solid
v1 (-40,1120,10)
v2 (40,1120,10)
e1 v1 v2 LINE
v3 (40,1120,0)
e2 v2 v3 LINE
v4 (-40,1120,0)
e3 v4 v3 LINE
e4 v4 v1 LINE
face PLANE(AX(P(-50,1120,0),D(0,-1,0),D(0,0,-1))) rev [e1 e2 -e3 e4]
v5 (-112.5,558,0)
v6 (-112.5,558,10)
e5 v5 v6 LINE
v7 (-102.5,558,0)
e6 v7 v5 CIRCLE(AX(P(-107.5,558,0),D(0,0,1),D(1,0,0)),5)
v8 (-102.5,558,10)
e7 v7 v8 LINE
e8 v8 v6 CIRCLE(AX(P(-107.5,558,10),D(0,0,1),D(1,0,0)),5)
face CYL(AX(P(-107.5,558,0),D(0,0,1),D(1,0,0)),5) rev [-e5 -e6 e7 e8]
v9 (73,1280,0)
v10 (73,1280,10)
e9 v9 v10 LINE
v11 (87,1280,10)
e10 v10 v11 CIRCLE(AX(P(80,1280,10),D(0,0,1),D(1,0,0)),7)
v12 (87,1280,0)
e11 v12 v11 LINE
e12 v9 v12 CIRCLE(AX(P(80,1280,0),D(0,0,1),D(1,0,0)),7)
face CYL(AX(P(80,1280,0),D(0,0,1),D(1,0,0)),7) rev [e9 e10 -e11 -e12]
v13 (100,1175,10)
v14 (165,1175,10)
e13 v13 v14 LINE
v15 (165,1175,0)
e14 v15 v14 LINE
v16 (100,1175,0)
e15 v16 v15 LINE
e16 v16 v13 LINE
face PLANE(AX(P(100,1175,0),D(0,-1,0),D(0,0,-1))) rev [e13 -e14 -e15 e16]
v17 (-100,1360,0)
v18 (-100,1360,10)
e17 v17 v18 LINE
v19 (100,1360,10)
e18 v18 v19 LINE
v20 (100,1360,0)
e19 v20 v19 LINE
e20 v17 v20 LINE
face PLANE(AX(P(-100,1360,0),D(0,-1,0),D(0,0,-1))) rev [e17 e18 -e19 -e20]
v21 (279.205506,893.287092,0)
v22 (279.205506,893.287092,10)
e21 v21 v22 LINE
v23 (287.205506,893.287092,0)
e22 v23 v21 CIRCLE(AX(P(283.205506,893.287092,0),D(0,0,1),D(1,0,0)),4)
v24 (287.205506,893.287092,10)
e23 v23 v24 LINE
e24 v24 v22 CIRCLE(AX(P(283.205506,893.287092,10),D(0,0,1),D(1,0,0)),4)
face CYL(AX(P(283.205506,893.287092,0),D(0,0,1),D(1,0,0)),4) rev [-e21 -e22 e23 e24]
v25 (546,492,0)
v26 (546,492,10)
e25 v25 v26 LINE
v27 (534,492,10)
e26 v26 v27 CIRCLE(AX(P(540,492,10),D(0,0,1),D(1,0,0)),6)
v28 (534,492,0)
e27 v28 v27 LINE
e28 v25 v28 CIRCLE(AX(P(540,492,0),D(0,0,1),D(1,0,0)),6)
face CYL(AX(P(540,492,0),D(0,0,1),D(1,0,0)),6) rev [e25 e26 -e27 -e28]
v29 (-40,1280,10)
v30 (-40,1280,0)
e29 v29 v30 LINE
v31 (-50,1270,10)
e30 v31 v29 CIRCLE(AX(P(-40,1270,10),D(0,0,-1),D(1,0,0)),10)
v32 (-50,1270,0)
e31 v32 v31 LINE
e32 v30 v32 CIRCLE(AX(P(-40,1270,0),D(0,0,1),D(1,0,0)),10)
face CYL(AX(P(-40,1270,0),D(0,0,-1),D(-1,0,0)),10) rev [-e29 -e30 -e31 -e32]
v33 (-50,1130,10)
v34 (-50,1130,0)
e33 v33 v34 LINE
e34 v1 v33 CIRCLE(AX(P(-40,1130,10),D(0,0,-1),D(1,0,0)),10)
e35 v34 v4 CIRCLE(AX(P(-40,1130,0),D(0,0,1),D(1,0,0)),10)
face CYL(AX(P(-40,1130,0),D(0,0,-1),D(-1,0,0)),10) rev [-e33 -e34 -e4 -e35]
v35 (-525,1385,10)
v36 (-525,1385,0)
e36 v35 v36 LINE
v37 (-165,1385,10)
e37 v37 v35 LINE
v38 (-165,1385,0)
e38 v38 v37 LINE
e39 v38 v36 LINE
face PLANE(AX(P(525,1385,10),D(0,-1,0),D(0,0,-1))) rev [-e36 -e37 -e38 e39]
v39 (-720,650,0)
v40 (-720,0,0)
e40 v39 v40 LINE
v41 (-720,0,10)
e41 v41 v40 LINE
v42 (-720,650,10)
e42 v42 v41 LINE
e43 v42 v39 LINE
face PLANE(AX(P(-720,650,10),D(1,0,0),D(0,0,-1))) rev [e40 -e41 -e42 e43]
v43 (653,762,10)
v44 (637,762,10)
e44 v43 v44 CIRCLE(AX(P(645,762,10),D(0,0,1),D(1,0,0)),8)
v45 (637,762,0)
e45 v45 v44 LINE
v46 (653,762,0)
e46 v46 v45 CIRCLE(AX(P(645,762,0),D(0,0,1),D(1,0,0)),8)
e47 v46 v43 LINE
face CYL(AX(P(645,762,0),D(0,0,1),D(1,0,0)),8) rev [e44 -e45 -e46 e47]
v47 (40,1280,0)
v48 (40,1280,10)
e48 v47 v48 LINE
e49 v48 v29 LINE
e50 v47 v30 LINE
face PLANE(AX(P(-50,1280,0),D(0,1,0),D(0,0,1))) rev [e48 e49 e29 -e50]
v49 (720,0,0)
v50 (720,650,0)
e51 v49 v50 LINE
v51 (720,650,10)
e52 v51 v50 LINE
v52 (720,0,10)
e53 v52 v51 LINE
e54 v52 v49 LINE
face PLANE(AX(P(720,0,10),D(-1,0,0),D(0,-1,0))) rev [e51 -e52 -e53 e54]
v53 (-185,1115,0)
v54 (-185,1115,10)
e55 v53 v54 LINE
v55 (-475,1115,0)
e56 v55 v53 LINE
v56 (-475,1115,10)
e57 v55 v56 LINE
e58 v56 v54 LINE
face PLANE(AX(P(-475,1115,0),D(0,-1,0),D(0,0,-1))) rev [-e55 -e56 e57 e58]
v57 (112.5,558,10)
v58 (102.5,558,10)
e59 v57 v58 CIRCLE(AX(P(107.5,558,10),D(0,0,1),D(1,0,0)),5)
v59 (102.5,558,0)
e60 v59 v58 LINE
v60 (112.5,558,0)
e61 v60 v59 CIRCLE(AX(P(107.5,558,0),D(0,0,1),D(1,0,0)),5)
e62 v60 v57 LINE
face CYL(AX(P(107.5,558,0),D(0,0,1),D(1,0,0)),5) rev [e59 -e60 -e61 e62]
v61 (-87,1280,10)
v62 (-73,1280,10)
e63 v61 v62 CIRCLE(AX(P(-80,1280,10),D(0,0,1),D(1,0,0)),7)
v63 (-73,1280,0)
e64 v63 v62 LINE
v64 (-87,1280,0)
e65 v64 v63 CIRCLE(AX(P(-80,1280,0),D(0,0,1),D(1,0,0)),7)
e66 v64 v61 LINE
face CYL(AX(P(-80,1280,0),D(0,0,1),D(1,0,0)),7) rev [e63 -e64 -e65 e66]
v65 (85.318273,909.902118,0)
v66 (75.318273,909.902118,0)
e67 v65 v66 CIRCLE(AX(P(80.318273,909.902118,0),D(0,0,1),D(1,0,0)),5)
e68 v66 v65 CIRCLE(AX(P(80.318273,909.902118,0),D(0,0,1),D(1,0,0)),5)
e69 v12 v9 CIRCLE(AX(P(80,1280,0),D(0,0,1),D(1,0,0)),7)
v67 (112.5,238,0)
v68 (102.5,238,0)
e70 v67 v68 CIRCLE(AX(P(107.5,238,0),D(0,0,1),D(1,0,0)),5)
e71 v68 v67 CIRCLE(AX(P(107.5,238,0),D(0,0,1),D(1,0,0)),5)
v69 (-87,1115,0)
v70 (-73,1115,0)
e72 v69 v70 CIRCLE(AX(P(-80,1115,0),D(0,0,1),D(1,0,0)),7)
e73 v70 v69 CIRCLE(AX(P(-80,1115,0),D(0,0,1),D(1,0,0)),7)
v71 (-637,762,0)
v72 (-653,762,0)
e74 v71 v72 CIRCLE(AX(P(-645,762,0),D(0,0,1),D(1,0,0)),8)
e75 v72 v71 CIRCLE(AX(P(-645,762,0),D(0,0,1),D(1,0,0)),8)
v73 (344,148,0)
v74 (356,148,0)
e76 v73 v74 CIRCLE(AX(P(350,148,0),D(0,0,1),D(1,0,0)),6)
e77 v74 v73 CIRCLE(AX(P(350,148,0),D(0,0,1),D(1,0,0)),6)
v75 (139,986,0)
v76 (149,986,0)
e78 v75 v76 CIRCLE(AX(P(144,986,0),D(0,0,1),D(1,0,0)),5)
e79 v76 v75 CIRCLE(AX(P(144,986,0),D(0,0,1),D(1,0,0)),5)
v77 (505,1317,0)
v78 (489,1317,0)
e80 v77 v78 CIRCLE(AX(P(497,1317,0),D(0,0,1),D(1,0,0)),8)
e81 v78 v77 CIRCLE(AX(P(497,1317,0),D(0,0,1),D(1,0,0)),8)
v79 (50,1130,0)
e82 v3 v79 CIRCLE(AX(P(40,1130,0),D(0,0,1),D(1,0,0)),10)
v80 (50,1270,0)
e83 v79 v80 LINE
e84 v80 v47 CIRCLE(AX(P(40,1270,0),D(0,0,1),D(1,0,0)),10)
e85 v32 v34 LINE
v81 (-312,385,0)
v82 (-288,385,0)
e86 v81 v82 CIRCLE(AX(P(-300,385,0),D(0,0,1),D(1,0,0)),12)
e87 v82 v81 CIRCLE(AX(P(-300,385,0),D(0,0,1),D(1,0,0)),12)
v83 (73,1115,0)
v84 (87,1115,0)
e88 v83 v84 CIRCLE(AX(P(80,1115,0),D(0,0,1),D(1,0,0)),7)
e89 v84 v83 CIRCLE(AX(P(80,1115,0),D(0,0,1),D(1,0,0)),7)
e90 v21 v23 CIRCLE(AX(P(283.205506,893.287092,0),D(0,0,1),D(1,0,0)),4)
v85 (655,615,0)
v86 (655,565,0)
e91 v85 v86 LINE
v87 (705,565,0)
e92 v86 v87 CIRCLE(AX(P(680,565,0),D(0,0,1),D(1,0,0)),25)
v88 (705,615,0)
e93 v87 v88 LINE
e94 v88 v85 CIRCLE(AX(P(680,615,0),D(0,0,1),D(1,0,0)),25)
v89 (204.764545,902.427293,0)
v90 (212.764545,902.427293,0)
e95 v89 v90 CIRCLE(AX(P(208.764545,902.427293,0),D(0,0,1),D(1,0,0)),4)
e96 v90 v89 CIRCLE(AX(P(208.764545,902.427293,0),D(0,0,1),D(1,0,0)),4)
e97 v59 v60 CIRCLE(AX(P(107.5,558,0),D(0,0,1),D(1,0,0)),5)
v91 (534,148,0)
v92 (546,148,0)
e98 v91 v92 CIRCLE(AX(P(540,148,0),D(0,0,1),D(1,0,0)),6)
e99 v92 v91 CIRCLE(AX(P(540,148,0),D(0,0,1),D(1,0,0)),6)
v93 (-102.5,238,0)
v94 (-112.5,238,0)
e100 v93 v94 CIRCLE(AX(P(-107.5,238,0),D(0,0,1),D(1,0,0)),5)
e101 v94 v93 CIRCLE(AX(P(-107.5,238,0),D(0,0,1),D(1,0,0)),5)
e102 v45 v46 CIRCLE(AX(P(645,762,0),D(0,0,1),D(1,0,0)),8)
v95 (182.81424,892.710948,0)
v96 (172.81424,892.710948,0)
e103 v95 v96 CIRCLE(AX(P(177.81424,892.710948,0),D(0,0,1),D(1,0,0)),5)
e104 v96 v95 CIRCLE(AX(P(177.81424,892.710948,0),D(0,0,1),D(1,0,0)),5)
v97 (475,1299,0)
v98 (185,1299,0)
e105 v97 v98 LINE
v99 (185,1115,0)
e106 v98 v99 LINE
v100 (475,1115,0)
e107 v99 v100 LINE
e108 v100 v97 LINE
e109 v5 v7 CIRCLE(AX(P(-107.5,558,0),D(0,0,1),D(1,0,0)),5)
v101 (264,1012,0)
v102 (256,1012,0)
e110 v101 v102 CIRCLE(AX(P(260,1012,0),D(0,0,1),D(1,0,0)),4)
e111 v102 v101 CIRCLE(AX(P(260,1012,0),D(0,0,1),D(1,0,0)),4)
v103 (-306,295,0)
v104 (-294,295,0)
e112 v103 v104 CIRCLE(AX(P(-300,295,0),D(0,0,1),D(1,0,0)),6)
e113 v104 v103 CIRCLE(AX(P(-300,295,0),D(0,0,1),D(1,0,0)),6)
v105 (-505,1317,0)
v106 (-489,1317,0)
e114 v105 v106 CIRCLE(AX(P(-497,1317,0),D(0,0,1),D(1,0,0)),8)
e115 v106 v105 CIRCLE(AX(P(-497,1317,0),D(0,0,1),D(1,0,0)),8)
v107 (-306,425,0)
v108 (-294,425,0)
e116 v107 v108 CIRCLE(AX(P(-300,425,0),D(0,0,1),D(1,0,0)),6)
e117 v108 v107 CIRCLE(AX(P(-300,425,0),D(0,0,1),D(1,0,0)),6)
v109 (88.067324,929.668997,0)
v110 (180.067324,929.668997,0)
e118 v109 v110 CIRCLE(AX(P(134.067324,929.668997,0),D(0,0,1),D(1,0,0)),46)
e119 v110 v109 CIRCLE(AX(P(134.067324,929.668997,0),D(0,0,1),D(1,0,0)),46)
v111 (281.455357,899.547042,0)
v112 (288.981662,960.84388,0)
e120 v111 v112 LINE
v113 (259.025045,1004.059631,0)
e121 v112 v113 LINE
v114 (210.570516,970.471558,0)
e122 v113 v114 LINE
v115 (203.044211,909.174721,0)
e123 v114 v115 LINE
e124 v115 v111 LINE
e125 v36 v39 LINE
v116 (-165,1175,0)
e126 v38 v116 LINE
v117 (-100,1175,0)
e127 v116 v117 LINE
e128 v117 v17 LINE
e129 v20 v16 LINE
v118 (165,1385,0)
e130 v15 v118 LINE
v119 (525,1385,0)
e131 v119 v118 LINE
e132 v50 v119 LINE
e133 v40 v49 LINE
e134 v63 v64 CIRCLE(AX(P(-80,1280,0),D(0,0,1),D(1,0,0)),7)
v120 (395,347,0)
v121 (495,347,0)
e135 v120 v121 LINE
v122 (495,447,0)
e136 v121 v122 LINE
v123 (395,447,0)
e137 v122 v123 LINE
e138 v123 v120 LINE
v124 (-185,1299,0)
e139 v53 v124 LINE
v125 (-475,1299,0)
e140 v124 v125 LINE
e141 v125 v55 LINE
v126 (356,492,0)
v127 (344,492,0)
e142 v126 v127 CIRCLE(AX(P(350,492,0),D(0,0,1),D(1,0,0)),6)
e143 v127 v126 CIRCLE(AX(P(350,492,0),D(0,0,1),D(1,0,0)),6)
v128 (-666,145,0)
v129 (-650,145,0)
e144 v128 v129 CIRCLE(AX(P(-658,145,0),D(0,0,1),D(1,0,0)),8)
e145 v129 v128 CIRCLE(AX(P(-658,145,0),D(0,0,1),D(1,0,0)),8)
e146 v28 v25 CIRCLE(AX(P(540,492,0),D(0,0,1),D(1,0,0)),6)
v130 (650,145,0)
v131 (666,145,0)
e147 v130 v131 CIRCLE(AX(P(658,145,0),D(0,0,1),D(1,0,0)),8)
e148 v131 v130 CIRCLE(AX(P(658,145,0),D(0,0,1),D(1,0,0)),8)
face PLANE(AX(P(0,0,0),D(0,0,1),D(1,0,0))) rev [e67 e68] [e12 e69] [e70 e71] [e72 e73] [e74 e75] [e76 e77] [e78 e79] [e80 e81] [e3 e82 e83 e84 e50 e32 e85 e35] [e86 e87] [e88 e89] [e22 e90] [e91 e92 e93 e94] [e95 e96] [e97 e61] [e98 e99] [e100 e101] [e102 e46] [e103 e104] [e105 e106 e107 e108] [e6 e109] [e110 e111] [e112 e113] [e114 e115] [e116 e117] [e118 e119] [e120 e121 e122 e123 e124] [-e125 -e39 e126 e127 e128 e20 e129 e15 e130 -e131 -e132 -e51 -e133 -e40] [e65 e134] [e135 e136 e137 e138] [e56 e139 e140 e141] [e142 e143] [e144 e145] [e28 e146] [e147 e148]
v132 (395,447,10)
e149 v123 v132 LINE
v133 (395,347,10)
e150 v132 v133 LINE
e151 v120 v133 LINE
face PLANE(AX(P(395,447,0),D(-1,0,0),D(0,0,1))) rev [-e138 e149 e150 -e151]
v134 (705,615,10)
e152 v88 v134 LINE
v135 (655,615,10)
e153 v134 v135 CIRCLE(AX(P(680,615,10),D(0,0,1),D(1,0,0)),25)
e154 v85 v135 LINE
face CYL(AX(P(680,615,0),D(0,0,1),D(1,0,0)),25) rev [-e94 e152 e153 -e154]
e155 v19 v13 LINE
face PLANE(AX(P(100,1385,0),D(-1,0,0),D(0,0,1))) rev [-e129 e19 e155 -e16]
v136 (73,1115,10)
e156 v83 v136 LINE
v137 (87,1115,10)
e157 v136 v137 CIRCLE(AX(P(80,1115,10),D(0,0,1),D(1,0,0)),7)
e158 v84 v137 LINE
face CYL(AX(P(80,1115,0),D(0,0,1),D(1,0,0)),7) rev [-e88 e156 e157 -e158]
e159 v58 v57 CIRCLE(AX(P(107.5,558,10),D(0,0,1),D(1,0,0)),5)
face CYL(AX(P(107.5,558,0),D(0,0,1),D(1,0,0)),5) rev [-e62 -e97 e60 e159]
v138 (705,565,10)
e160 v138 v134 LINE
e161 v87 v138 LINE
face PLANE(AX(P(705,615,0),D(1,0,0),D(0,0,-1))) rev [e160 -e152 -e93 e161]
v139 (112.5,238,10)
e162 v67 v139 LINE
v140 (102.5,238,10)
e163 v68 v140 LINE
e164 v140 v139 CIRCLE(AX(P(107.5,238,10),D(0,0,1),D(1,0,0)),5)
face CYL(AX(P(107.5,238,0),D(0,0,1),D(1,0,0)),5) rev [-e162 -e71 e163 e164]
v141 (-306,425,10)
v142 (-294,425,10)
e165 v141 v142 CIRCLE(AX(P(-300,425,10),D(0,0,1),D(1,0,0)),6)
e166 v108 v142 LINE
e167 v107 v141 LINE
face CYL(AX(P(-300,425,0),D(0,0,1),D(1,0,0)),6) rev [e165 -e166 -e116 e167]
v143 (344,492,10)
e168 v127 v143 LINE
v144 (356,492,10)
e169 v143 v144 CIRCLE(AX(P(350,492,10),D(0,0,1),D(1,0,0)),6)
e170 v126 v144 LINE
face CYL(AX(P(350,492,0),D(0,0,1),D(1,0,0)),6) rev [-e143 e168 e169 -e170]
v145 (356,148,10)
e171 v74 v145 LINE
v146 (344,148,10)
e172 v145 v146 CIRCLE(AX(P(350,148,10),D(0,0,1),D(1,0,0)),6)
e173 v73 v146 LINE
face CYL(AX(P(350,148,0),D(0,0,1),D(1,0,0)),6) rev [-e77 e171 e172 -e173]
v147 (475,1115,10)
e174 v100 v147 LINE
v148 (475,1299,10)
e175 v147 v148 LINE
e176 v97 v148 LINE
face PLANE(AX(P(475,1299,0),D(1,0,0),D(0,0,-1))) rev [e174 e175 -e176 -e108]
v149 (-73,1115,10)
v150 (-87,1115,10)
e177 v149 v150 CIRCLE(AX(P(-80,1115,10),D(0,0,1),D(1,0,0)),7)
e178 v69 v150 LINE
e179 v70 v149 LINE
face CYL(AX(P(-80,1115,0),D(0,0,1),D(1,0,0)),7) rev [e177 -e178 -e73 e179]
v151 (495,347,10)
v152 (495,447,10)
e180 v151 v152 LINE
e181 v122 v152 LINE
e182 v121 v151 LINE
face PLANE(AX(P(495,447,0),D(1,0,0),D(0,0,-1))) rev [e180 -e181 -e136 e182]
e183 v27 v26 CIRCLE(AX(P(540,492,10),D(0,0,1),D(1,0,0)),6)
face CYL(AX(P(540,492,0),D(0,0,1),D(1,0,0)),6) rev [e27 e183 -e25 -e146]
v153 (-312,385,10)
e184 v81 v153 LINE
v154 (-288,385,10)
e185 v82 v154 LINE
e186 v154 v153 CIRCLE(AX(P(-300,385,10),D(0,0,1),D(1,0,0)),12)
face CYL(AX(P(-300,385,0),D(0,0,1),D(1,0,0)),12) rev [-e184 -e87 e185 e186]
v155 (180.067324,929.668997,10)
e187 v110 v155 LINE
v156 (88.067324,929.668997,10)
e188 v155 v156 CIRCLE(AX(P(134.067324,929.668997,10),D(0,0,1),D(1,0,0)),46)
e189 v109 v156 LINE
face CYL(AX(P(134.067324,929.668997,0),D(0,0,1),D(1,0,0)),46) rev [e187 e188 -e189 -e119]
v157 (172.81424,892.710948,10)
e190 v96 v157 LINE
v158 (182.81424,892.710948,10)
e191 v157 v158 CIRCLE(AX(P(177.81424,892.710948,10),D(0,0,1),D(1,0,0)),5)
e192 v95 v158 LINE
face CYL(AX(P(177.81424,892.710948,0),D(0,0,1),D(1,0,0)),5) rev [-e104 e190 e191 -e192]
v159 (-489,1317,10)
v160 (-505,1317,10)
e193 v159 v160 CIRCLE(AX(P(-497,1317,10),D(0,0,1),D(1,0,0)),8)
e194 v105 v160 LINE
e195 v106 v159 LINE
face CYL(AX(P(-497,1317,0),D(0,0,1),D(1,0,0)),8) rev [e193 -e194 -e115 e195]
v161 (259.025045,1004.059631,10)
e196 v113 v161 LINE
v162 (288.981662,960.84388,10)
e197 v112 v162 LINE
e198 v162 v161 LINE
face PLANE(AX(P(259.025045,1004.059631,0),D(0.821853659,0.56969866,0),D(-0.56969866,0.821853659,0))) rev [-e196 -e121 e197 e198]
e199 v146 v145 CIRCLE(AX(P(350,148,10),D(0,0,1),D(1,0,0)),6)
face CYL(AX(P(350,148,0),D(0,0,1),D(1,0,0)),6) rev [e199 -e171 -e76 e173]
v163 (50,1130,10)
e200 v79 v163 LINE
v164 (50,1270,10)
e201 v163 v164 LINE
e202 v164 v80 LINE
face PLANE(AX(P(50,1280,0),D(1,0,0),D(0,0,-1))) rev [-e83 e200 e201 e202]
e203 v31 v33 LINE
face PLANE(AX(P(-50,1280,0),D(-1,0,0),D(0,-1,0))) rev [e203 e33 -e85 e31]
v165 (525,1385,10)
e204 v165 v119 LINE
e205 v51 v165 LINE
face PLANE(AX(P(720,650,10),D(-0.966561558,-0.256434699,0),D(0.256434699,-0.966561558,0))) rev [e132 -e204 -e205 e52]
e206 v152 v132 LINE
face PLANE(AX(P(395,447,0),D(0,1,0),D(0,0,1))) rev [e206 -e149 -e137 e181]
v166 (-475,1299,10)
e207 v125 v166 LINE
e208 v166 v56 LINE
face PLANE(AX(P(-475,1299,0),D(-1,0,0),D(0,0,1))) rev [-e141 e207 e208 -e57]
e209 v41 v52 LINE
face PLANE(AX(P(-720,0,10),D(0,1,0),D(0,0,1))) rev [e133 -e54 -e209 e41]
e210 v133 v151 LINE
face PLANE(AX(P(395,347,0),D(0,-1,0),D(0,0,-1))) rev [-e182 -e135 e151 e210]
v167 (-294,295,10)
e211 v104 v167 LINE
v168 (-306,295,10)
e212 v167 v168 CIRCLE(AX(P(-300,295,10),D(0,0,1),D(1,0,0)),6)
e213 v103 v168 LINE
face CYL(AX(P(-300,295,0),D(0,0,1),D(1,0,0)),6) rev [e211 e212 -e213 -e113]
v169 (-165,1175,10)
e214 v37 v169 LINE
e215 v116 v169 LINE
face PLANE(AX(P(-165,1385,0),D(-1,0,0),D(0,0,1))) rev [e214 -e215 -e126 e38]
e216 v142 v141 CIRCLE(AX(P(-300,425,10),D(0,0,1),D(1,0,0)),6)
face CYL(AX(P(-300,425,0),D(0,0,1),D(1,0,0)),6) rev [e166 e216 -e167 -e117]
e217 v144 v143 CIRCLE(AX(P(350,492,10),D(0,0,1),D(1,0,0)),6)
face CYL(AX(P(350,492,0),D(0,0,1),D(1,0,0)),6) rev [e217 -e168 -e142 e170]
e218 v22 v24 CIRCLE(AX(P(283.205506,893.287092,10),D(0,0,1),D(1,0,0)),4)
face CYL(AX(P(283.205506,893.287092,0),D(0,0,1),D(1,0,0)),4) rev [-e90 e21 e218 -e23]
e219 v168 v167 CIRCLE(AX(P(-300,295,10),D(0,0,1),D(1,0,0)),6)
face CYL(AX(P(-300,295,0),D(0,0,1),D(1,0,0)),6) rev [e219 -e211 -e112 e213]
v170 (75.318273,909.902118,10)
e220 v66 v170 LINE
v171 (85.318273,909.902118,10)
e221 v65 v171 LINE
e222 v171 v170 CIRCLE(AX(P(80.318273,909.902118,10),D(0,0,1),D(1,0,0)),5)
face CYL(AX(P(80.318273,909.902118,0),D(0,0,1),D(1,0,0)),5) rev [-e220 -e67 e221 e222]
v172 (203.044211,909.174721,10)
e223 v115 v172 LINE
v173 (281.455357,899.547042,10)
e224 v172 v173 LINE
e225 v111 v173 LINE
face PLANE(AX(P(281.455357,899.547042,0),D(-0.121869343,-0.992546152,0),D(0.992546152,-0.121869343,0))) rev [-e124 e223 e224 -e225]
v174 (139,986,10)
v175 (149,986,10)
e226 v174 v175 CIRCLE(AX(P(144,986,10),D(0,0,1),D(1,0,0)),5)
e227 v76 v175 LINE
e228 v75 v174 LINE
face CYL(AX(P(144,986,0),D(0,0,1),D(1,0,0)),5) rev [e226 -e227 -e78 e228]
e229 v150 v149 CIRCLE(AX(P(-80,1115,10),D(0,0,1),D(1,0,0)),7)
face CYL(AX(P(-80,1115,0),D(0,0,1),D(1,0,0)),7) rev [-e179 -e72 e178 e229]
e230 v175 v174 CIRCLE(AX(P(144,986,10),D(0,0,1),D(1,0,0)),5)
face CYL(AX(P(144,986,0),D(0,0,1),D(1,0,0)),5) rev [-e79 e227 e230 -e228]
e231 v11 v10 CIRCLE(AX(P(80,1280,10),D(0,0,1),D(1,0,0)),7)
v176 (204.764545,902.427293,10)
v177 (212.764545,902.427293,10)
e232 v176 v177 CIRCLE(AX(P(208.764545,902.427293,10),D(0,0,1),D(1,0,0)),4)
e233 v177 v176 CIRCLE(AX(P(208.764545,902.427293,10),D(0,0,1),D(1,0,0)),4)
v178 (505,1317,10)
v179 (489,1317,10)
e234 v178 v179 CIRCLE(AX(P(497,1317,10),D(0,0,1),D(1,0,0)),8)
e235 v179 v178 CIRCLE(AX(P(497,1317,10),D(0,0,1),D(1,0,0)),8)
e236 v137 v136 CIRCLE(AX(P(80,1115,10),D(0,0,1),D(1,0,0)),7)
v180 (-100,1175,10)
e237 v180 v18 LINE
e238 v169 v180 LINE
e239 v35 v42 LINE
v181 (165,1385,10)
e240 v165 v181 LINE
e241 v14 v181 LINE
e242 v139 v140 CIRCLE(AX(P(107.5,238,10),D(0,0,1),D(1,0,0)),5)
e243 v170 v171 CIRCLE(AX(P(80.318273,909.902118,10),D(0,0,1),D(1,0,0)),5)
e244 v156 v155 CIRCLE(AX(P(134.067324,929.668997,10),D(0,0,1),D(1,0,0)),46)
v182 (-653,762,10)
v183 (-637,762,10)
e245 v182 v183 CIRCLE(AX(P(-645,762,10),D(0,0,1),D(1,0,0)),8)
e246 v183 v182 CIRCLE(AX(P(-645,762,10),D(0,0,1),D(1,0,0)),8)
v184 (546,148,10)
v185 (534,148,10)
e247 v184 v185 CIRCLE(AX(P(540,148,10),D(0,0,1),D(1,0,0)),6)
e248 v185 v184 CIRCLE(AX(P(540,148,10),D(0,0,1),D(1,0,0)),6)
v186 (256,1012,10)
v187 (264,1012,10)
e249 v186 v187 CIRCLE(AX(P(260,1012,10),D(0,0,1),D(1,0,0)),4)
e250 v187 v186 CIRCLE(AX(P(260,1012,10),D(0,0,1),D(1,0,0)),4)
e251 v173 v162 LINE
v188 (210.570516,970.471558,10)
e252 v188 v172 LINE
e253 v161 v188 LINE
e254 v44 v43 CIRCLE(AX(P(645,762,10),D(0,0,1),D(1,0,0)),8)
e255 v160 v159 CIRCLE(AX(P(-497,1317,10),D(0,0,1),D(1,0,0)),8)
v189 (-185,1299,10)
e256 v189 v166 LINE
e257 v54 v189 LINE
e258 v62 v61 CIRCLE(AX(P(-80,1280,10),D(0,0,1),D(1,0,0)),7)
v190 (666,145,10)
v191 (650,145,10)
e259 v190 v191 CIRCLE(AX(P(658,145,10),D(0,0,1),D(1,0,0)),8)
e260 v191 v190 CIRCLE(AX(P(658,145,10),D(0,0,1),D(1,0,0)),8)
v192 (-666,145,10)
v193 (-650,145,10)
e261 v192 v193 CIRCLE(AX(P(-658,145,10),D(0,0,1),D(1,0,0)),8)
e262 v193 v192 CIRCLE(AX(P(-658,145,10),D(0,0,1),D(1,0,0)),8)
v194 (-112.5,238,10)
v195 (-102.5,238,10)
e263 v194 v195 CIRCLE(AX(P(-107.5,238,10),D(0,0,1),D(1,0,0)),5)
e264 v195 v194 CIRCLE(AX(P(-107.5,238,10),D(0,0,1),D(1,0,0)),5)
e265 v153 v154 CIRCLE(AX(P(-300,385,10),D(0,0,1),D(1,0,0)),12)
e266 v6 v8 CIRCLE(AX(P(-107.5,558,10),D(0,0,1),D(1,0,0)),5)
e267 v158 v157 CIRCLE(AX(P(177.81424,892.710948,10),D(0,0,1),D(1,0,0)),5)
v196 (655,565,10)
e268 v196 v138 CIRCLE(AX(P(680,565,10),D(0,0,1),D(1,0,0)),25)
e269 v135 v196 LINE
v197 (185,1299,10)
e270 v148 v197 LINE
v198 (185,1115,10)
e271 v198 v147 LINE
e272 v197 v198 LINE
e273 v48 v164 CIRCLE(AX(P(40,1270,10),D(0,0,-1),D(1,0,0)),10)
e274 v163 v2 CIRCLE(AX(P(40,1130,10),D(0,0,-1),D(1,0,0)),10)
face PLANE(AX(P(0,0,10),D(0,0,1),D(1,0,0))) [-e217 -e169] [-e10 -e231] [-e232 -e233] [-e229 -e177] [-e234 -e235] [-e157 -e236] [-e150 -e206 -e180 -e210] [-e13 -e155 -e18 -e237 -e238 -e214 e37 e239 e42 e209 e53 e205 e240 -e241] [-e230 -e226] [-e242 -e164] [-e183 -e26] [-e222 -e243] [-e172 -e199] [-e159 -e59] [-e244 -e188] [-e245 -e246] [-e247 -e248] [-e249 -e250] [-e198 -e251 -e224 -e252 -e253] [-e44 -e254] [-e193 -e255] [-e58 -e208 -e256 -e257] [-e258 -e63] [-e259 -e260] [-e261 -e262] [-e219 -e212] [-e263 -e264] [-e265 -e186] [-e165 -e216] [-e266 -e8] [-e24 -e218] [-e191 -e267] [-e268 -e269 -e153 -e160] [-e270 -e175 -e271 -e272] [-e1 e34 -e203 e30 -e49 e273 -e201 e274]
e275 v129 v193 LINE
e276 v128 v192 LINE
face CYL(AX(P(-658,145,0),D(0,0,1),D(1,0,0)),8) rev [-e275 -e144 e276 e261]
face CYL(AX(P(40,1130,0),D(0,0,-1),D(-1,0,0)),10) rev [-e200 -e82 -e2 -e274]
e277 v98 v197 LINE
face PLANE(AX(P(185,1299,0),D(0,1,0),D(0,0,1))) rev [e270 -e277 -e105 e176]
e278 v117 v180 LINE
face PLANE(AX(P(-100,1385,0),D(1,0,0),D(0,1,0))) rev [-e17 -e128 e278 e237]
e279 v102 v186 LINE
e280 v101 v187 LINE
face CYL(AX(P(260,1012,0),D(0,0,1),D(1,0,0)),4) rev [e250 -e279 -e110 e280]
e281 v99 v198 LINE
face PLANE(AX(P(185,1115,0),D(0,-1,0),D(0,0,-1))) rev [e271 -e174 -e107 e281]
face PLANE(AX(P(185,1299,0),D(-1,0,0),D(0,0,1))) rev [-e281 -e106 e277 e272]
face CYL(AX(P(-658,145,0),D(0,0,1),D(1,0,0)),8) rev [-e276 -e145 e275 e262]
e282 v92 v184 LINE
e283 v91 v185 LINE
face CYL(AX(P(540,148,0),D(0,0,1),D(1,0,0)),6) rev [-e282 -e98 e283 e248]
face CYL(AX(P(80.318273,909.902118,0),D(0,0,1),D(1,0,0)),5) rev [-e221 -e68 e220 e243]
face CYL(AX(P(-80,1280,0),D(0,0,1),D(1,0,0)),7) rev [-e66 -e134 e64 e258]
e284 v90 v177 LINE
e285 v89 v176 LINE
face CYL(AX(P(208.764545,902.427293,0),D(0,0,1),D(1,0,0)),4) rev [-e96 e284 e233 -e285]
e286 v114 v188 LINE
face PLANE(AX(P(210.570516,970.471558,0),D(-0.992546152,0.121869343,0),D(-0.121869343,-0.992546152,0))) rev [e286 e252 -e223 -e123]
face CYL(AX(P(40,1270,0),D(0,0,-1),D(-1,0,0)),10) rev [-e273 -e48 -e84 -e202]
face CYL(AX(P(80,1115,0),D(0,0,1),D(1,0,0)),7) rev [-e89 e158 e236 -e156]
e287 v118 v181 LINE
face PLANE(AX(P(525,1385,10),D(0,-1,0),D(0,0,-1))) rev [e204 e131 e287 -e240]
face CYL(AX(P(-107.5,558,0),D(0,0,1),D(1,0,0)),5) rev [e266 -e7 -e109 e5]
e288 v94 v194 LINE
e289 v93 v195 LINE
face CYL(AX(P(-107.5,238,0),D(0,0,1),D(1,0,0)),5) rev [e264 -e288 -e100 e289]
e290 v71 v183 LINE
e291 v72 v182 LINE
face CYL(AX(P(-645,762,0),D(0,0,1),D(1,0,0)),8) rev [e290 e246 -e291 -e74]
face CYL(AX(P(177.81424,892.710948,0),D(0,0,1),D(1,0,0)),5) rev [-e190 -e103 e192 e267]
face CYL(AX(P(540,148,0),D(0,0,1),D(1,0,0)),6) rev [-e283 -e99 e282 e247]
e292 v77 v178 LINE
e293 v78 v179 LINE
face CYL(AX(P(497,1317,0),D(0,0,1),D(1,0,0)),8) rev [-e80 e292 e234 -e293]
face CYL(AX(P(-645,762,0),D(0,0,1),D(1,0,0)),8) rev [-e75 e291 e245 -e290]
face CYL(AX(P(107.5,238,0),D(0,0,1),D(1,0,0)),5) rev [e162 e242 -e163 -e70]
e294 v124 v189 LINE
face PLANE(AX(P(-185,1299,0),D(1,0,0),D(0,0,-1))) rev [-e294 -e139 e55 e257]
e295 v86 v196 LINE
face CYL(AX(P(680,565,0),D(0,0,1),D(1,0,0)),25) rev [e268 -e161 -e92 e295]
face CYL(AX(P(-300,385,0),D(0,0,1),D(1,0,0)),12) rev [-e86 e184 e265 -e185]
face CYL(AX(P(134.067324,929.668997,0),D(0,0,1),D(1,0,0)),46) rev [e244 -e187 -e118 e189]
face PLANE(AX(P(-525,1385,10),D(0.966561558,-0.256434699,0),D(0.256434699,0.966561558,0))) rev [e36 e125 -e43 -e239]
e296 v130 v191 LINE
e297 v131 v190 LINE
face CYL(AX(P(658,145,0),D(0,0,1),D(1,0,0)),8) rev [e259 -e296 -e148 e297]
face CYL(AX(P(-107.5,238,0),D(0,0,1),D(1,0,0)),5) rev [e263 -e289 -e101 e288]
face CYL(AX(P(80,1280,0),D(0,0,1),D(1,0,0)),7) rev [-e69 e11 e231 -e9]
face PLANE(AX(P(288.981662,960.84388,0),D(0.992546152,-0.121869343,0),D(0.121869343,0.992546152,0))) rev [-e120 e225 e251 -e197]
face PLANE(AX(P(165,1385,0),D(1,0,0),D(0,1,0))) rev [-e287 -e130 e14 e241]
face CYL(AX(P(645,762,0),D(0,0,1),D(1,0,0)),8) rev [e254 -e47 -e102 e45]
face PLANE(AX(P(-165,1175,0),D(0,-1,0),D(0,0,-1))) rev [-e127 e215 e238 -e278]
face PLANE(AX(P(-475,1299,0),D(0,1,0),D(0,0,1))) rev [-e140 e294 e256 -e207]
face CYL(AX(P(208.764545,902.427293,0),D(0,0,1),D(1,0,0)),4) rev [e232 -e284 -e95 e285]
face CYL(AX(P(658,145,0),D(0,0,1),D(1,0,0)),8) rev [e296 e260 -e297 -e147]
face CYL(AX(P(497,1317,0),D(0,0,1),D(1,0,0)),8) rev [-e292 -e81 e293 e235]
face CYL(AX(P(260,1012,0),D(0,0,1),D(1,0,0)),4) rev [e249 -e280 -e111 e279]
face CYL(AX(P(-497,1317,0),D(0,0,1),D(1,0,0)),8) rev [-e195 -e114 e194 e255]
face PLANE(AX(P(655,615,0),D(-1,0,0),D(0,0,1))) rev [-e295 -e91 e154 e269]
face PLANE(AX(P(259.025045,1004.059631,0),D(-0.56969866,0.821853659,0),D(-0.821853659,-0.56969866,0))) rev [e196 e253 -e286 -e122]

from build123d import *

# Parameters (mm, degrees)
BOSS_EXTRUDE1_DEPTH  = 10
SKETCH2_R            = 8
CUT_EXTRUDE1_DEPTH   = 10
LPATTERN1_COUNT      = 2
LPATTERN1_PITCH      = 1316
SKETCH3_R            = 8
CUT_EXTRUDE2_DEPTH   = 10
LPATTERN2_COUNT      = 2
LPATTERN2_PITCH      = 1290
SKETCH4_R            = 8
CUT_EXTRUDE3_DEPTH   = 10
LPATTERN3_COUNT      = 2
LPATTERN3_PITCH      = 994
CUT_EXTRUDE4_DEPTH   = 10
SKETCH6_W            = 100
SKETCH6_H            = 100
CUT_EXTRUDE5_DEPTH   = 10
SKETCH7_R            = 6
CUT_EXTRUDE6_DEPTH   = 10
LPATTERN4_COUNT      = 2
LPATTERN4_PITCH      = 190
LPATTERN4_COUNT_DIR2 = 2
LPATTERN4_PITCH_DIR2 = 344
SKETCH8_R            = 5
CUT_EXTRUDE7_DEPTH   = 10
LPATTERN5_COUNT      = 2
LPATTERN5_PITCH      = 320
LPATTERN5_COUNT_DIR2 = 2
LPATTERN5_PITCH_DIR2 = 215
SKETCH9_W            = 290
SKETCH9_H            = 184
CUT_EXTRUDE8_DEPTH   = 10
SKETCH10_W           = 100
SKETCH10_H           = 160
CUT_EXTRUDE9_DEPTH   = 10
FILLET1_R            = 10
SKETCH11_R           = 7
CUT_EXTRUDE10_DEPTH  = 10
LPATTERN7_COUNT      = 2
LPATTERN7_PITCH      = 160
LPATTERN7_COUNT_DIR2 = 2
LPATTERN7_PITCH_DIR2 = 165
SKETCH12_R           = 5
CUT_EXTRUDE11_DEPTH  = 10
SKETCH14_R           = 46
CUT_EXTRUDE12_DEPTH  = 10
SKETCH15_R           = 5
CUT_EXTRUDE13_DEPTH  = 10
LPATTERN8_COUNT      = 2
LPATTERN8_PITCH      = 99
SKETCH16_R           = 4
CUT_EXTRUDE14_DEPTH  = 10
CUT_EXTRUDE15_DEPTH  = 10
SKETCH18_R           = 4
CUT_EXTRUDE16_DEPTH  = 10
LPATTERN9_COUNT      = 2
LPATTERN9_PITCH      = 75
SKETCH19_R           = 6
CUT_EXTRUDE17_DEPTH  = 10
LPATTERN10_COUNT     = 2
LPATTERN10_PITCH     = 130
SKETCH20_R           = 12
CUT_EXTRUDE18_DEPTH  = 10
LPATTERN11_COUNT     = 2
LPATTERN11_PITCH     = 660
SKETCH21_W           = 65
SKETCH21_H           = 210
CUT_EXTRUDE19_DEPTH  = 10
SKETCH22_W           = 65
SKETCH22_H           = 210
CUT_EXTRUDE20_DEPTH  = 10
SKETCH23_W           = 200
SKETCH23_H           = 25
CUT_EXTRUDE21_DEPTH  = 10


with BuildPart() as part:
    # Sketch1 → Boss-Extrude1 (new body)
    with BuildSketch(Plane.XY):
        Polygon((-720, 0), (720, 0), (720, 650), (525, 1385), (-525, 1385), (-720, 650), align=None)
    extrude(amount=BOSS_EXTRUDE1_DEPTH)

    # Sketch2 → Cut-Extrude1 (cut)
    with BuildSketch(Plane.XY.offset(10)):
        with Locations((-658, 145)):
            Circle(SKETCH2_R)
    cut_extrude1 = extrude(amount=-CUT_EXTRUDE1_DEPTH, mode=Mode.SUBTRACT)

    # LPattern1: Cut-Extrude1 ×2
    with Locations(*[(i * LPATTERN1_PITCH, 0, 0) for i in range(1, LPATTERN1_COUNT)]):
        add(cut_extrude1, mode=Mode.SUBTRACT)

    # Sketch3 → Cut-Extrude2 (cut)
    with BuildSketch(Plane.XY.offset(10)):
        with Locations((-645, 762)):
            Circle(SKETCH3_R)
    cut_extrude2 = extrude(amount=-CUT_EXTRUDE2_DEPTH, mode=Mode.SUBTRACT)

    # LPattern2: Cut-Extrude2 ×2
    with Locations(*[(i * LPATTERN2_PITCH, 0, 0) for i in range(1, LPATTERN2_COUNT)]):
        add(cut_extrude2, mode=Mode.SUBTRACT)

    # Sketch4 → Cut-Extrude3 (cut)
    with BuildSketch(Plane.XY.offset(10)):
        with Locations((-497, 1317)):
            Circle(SKETCH4_R)
    cut_extrude3 = extrude(amount=-CUT_EXTRUDE3_DEPTH, mode=Mode.SUBTRACT)

    # LPattern3: Cut-Extrude3 ×2
    with Locations(*[(i * LPATTERN3_PITCH, 0, 0) for i in range(1, LPATTERN3_COUNT)]):
        add(cut_extrude3, mode=Mode.SUBTRACT)

    # Sketch5 → Cut-Extrude4 (cut)
    with BuildSketch(Plane.XY.offset(10)):
        with BuildLine():
            Line((655, 615), (655, 565))
            ThreePointArc((655, 565), (680, 540), (705, 565))
            Line((705, 565), (705, 615))
            ThreePointArc((705, 615), (680, 640), (655, 615))
        make_face()
    extrude(amount=-CUT_EXTRUDE4_DEPTH, mode=Mode.SUBTRACT)

    # Sketch6 → Cut-Extrude5 (cut)
    with BuildSketch(Plane.XY.offset(10)):
        with Locations((445, 397)):
            Rectangle(SKETCH6_W, SKETCH6_H)
    extrude(amount=-CUT_EXTRUDE5_DEPTH, mode=Mode.SUBTRACT)

    # Sketch7 → Cut-Extrude6 (cut)
    with BuildSketch(Plane.XY.offset(10)):
        with Locations((540, 492)):
            Circle(SKETCH7_R)
    cut_extrude6 = extrude(amount=-CUT_EXTRUDE6_DEPTH, mode=Mode.SUBTRACT)

    # LPattern4: Cut-Extrude6 2 × 2
    with Locations(*[(-i * LPATTERN4_PITCH, -j * LPATTERN4_PITCH_DIR2, 0) for i in range(LPATTERN4_COUNT) for j in range(LPATTERN4_COUNT_DIR2) if (i, j) != (0, 0)]):
        add(cut_extrude6, mode=Mode.SUBTRACT)

    # Sketch8 → Cut-Extrude7 (cut)
    with BuildSketch(Plane.XY.offset(10)):
        with Locations((107.5, 238)):
            Circle(SKETCH8_R)
    cut_extrude7 = extrude(amount=-CUT_EXTRUDE7_DEPTH, mode=Mode.SUBTRACT)

    # LPattern5: Cut-Extrude7 2 × 2
    with Locations(*[(-j * LPATTERN5_PITCH_DIR2, i * LPATTERN5_PITCH, 0) for i in range(LPATTERN5_COUNT) for j in range(LPATTERN5_COUNT_DIR2) if (i, j) != (0, 0)]):
        add(cut_extrude7, mode=Mode.SUBTRACT)

    # Sketch9 → Cut-Extrude8 (cut)
    with BuildSketch(Plane.XY.offset(10)):
        with Locations((-330, 1207)):
            Rectangle(SKETCH9_W, SKETCH9_H)
    cut_extrude8 = extrude(amount=-CUT_EXTRUDE8_DEPTH, mode=Mode.SUBTRACT)

    # Sketch10 → Cut-Extrude9 (cut)
    with BuildSketch(Plane.XY.offset(10)):
        with Locations((0, 1200)):
            Rectangle(SKETCH10_W, SKETCH10_H)
    extrude(amount=-CUT_EXTRUDE9_DEPTH, mode=Mode.SUBTRACT)

    # Fillet1
    fillet1_edges = [part.edges().sort_by_distance(p)[0] for p in [
        (-50, 1120, 5),
        (-50, 1280, 5),
        (50, 1280, 5),
        (50, 1120, 5),
    ]]
    fillet(fillet1_edges, radius=FILLET1_R)

    # Sketch11 → Cut-Extrude10 (cut)
    with BuildSketch(Plane.XY.offset(10)):
        with Locations((80, 1280)):
            Circle(SKETCH11_R)
    cut_extrude10 = extrude(amount=-CUT_EXTRUDE10_DEPTH, mode=Mode.SUBTRACT)

    # LPattern7: Cut-Extrude10 2 × 2
    with Locations(*[(-i * LPATTERN7_PITCH, -j * LPATTERN7_PITCH_DIR2, 0) for i in range(LPATTERN7_COUNT) for j in range(LPATTERN7_COUNT_DIR2) if (i, j) != (0, 0)]):
        add(cut_extrude10, mode=Mode.SUBTRACT)

    # Sketch12 → Cut-Extrude11 (cut)
    with BuildSketch(Plane.XY.offset(10)):
        with Locations((144, 986)):
            Circle(SKETCH12_R)
    extrude(amount=-CUT_EXTRUDE11_DEPTH, mode=Mode.SUBTRACT)

    # Sketch14 → Cut-Extrude12 (cut)
    with BuildSketch(Plane.XY.offset(10)):
        with Locations((134.067324237, 929.668996528)):
            Circle(SKETCH14_R)
    extrude(amount=-CUT_EXTRUDE12_DEPTH, mode=Mode.SUBTRACT)

    # Sketch15 → Cut-Extrude13 (cut)
    with BuildSketch(Plane.XY.offset(10)):
        with Locations((80.318272947, 909.902118035)):
            Circle(SKETCH15_R)
    cut_extrude13 = extrude(amount=-CUT_EXTRUDE13_DEPTH, mode=Mode.SUBTRACT)

    # LPattern8: Cut-Extrude13 ×2
    with Locations(*[Vector(0.9848077530122089, -0.17364817766692592, 0) * (i * LPATTERN8_PITCH) for i in range(1, LPATTERN8_COUNT)]):
        add(cut_extrude13, mode=Mode.SUBTRACT)

    # Sketch16 → Cut-Extrude14 (cut)
    with BuildSketch(Plane.XY.offset(10)):
        with Locations((260, 1012)):
            Circle(SKETCH16_R)
    extrude(amount=-CUT_EXTRUDE14_DEPTH, mode=Mode.SUBTRACT)

    # Sketch17 → Cut-Extrude15 (cut)
    with BuildSketch(Plane.XY.offset(10)):
        Polygon((259.025045253, 1004.059630787), (210.570516199, 970.471558288), (203.044210897, 909.174720581), (281.455356876, 899.547042452), (288.981662179, 960.843880159), align=None)
    extrude(amount=-CUT_EXTRUDE15_DEPTH, mode=Mode.SUBTRACT)

    # Sketch18 → Cut-Extrude16 (cut)
    with BuildSketch(Plane.XY.offset(10)):
        with Locations((208.764544822, 902.427292939)):
            Circle(SKETCH18_R)
    cut_extrude16 = extrude(amount=-CUT_EXTRUDE16_DEPTH, mode=Mode.SUBTRACT)

    # LPattern9: Cut-Extrude16 ×2
    with Locations(*[Vector(0.9925461516413229, -0.12186934340514104, 0) * (i * LPATTERN9_PITCH) for i in range(1, LPATTERN9_COUNT)]):
        add(cut_extrude16, mode=Mode.SUBTRACT)

    # Sketch19 → Cut-Extrude17 (cut)
    with BuildSketch(Plane.XY.offset(10)):
        with Locations((-300, 295)):
            Circle(SKETCH19_R)
    cut_extrude17 = extrude(amount=-CUT_EXTRUDE17_DEPTH, mode=Mode.SUBTRACT)

    # LPattern10: Cut-Extrude17 ×2
    with Locations(*[(0, i * LPATTERN10_PITCH, 0) for i in range(1, LPATTERN10_COUNT)]):
        add(cut_extrude17, mode=Mode.SUBTRACT)

    # Sketch20 → Cut-Extrude18 (cut)
    with BuildSketch(Plane.XY.offset(10)):
        with Locations((-300, 385)):
            Circle(SKETCH20_R)
    extrude(amount=-CUT_EXTRUDE18_DEPTH, mode=Mode.SUBTRACT)

    # LPattern11: Cut-Extrude8 ×2
    with Locations(*[(i * LPATTERN11_PITCH, 0, 0) for i in range(1, LPATTERN11_COUNT)]):
        add(cut_extrude8, mode=Mode.SUBTRACT)

    # Sketch21 → Cut-Extrude19 (cut)
    with BuildSketch(Plane.XY.offset(10)):
        with Locations((132.5, 1280)):
            Rectangle(SKETCH21_W, SKETCH21_H)
    extrude(amount=-CUT_EXTRUDE19_DEPTH, mode=Mode.SUBTRACT)

    # Sketch22 → Cut-Extrude20 (cut)
    with BuildSketch(Plane.XY.offset(10)):
        with Locations((-132.5, 1280)):
            Rectangle(SKETCH22_W, SKETCH22_H)
    extrude(amount=-CUT_EXTRUDE20_DEPTH, mode=Mode.SUBTRACT)

    # Sketch23 → Cut-Extrude21 (cut)
    with BuildSketch(Plane.XY.offset(10)):
        with Locations((0, 1372.5)):
            Rectangle(SKETCH23_W, SKETCH23_H)
    extrude(amount=-CUT_EXTRUDE21_DEPTH, mode=Mode.SUBTRACT)


solid = part.part
